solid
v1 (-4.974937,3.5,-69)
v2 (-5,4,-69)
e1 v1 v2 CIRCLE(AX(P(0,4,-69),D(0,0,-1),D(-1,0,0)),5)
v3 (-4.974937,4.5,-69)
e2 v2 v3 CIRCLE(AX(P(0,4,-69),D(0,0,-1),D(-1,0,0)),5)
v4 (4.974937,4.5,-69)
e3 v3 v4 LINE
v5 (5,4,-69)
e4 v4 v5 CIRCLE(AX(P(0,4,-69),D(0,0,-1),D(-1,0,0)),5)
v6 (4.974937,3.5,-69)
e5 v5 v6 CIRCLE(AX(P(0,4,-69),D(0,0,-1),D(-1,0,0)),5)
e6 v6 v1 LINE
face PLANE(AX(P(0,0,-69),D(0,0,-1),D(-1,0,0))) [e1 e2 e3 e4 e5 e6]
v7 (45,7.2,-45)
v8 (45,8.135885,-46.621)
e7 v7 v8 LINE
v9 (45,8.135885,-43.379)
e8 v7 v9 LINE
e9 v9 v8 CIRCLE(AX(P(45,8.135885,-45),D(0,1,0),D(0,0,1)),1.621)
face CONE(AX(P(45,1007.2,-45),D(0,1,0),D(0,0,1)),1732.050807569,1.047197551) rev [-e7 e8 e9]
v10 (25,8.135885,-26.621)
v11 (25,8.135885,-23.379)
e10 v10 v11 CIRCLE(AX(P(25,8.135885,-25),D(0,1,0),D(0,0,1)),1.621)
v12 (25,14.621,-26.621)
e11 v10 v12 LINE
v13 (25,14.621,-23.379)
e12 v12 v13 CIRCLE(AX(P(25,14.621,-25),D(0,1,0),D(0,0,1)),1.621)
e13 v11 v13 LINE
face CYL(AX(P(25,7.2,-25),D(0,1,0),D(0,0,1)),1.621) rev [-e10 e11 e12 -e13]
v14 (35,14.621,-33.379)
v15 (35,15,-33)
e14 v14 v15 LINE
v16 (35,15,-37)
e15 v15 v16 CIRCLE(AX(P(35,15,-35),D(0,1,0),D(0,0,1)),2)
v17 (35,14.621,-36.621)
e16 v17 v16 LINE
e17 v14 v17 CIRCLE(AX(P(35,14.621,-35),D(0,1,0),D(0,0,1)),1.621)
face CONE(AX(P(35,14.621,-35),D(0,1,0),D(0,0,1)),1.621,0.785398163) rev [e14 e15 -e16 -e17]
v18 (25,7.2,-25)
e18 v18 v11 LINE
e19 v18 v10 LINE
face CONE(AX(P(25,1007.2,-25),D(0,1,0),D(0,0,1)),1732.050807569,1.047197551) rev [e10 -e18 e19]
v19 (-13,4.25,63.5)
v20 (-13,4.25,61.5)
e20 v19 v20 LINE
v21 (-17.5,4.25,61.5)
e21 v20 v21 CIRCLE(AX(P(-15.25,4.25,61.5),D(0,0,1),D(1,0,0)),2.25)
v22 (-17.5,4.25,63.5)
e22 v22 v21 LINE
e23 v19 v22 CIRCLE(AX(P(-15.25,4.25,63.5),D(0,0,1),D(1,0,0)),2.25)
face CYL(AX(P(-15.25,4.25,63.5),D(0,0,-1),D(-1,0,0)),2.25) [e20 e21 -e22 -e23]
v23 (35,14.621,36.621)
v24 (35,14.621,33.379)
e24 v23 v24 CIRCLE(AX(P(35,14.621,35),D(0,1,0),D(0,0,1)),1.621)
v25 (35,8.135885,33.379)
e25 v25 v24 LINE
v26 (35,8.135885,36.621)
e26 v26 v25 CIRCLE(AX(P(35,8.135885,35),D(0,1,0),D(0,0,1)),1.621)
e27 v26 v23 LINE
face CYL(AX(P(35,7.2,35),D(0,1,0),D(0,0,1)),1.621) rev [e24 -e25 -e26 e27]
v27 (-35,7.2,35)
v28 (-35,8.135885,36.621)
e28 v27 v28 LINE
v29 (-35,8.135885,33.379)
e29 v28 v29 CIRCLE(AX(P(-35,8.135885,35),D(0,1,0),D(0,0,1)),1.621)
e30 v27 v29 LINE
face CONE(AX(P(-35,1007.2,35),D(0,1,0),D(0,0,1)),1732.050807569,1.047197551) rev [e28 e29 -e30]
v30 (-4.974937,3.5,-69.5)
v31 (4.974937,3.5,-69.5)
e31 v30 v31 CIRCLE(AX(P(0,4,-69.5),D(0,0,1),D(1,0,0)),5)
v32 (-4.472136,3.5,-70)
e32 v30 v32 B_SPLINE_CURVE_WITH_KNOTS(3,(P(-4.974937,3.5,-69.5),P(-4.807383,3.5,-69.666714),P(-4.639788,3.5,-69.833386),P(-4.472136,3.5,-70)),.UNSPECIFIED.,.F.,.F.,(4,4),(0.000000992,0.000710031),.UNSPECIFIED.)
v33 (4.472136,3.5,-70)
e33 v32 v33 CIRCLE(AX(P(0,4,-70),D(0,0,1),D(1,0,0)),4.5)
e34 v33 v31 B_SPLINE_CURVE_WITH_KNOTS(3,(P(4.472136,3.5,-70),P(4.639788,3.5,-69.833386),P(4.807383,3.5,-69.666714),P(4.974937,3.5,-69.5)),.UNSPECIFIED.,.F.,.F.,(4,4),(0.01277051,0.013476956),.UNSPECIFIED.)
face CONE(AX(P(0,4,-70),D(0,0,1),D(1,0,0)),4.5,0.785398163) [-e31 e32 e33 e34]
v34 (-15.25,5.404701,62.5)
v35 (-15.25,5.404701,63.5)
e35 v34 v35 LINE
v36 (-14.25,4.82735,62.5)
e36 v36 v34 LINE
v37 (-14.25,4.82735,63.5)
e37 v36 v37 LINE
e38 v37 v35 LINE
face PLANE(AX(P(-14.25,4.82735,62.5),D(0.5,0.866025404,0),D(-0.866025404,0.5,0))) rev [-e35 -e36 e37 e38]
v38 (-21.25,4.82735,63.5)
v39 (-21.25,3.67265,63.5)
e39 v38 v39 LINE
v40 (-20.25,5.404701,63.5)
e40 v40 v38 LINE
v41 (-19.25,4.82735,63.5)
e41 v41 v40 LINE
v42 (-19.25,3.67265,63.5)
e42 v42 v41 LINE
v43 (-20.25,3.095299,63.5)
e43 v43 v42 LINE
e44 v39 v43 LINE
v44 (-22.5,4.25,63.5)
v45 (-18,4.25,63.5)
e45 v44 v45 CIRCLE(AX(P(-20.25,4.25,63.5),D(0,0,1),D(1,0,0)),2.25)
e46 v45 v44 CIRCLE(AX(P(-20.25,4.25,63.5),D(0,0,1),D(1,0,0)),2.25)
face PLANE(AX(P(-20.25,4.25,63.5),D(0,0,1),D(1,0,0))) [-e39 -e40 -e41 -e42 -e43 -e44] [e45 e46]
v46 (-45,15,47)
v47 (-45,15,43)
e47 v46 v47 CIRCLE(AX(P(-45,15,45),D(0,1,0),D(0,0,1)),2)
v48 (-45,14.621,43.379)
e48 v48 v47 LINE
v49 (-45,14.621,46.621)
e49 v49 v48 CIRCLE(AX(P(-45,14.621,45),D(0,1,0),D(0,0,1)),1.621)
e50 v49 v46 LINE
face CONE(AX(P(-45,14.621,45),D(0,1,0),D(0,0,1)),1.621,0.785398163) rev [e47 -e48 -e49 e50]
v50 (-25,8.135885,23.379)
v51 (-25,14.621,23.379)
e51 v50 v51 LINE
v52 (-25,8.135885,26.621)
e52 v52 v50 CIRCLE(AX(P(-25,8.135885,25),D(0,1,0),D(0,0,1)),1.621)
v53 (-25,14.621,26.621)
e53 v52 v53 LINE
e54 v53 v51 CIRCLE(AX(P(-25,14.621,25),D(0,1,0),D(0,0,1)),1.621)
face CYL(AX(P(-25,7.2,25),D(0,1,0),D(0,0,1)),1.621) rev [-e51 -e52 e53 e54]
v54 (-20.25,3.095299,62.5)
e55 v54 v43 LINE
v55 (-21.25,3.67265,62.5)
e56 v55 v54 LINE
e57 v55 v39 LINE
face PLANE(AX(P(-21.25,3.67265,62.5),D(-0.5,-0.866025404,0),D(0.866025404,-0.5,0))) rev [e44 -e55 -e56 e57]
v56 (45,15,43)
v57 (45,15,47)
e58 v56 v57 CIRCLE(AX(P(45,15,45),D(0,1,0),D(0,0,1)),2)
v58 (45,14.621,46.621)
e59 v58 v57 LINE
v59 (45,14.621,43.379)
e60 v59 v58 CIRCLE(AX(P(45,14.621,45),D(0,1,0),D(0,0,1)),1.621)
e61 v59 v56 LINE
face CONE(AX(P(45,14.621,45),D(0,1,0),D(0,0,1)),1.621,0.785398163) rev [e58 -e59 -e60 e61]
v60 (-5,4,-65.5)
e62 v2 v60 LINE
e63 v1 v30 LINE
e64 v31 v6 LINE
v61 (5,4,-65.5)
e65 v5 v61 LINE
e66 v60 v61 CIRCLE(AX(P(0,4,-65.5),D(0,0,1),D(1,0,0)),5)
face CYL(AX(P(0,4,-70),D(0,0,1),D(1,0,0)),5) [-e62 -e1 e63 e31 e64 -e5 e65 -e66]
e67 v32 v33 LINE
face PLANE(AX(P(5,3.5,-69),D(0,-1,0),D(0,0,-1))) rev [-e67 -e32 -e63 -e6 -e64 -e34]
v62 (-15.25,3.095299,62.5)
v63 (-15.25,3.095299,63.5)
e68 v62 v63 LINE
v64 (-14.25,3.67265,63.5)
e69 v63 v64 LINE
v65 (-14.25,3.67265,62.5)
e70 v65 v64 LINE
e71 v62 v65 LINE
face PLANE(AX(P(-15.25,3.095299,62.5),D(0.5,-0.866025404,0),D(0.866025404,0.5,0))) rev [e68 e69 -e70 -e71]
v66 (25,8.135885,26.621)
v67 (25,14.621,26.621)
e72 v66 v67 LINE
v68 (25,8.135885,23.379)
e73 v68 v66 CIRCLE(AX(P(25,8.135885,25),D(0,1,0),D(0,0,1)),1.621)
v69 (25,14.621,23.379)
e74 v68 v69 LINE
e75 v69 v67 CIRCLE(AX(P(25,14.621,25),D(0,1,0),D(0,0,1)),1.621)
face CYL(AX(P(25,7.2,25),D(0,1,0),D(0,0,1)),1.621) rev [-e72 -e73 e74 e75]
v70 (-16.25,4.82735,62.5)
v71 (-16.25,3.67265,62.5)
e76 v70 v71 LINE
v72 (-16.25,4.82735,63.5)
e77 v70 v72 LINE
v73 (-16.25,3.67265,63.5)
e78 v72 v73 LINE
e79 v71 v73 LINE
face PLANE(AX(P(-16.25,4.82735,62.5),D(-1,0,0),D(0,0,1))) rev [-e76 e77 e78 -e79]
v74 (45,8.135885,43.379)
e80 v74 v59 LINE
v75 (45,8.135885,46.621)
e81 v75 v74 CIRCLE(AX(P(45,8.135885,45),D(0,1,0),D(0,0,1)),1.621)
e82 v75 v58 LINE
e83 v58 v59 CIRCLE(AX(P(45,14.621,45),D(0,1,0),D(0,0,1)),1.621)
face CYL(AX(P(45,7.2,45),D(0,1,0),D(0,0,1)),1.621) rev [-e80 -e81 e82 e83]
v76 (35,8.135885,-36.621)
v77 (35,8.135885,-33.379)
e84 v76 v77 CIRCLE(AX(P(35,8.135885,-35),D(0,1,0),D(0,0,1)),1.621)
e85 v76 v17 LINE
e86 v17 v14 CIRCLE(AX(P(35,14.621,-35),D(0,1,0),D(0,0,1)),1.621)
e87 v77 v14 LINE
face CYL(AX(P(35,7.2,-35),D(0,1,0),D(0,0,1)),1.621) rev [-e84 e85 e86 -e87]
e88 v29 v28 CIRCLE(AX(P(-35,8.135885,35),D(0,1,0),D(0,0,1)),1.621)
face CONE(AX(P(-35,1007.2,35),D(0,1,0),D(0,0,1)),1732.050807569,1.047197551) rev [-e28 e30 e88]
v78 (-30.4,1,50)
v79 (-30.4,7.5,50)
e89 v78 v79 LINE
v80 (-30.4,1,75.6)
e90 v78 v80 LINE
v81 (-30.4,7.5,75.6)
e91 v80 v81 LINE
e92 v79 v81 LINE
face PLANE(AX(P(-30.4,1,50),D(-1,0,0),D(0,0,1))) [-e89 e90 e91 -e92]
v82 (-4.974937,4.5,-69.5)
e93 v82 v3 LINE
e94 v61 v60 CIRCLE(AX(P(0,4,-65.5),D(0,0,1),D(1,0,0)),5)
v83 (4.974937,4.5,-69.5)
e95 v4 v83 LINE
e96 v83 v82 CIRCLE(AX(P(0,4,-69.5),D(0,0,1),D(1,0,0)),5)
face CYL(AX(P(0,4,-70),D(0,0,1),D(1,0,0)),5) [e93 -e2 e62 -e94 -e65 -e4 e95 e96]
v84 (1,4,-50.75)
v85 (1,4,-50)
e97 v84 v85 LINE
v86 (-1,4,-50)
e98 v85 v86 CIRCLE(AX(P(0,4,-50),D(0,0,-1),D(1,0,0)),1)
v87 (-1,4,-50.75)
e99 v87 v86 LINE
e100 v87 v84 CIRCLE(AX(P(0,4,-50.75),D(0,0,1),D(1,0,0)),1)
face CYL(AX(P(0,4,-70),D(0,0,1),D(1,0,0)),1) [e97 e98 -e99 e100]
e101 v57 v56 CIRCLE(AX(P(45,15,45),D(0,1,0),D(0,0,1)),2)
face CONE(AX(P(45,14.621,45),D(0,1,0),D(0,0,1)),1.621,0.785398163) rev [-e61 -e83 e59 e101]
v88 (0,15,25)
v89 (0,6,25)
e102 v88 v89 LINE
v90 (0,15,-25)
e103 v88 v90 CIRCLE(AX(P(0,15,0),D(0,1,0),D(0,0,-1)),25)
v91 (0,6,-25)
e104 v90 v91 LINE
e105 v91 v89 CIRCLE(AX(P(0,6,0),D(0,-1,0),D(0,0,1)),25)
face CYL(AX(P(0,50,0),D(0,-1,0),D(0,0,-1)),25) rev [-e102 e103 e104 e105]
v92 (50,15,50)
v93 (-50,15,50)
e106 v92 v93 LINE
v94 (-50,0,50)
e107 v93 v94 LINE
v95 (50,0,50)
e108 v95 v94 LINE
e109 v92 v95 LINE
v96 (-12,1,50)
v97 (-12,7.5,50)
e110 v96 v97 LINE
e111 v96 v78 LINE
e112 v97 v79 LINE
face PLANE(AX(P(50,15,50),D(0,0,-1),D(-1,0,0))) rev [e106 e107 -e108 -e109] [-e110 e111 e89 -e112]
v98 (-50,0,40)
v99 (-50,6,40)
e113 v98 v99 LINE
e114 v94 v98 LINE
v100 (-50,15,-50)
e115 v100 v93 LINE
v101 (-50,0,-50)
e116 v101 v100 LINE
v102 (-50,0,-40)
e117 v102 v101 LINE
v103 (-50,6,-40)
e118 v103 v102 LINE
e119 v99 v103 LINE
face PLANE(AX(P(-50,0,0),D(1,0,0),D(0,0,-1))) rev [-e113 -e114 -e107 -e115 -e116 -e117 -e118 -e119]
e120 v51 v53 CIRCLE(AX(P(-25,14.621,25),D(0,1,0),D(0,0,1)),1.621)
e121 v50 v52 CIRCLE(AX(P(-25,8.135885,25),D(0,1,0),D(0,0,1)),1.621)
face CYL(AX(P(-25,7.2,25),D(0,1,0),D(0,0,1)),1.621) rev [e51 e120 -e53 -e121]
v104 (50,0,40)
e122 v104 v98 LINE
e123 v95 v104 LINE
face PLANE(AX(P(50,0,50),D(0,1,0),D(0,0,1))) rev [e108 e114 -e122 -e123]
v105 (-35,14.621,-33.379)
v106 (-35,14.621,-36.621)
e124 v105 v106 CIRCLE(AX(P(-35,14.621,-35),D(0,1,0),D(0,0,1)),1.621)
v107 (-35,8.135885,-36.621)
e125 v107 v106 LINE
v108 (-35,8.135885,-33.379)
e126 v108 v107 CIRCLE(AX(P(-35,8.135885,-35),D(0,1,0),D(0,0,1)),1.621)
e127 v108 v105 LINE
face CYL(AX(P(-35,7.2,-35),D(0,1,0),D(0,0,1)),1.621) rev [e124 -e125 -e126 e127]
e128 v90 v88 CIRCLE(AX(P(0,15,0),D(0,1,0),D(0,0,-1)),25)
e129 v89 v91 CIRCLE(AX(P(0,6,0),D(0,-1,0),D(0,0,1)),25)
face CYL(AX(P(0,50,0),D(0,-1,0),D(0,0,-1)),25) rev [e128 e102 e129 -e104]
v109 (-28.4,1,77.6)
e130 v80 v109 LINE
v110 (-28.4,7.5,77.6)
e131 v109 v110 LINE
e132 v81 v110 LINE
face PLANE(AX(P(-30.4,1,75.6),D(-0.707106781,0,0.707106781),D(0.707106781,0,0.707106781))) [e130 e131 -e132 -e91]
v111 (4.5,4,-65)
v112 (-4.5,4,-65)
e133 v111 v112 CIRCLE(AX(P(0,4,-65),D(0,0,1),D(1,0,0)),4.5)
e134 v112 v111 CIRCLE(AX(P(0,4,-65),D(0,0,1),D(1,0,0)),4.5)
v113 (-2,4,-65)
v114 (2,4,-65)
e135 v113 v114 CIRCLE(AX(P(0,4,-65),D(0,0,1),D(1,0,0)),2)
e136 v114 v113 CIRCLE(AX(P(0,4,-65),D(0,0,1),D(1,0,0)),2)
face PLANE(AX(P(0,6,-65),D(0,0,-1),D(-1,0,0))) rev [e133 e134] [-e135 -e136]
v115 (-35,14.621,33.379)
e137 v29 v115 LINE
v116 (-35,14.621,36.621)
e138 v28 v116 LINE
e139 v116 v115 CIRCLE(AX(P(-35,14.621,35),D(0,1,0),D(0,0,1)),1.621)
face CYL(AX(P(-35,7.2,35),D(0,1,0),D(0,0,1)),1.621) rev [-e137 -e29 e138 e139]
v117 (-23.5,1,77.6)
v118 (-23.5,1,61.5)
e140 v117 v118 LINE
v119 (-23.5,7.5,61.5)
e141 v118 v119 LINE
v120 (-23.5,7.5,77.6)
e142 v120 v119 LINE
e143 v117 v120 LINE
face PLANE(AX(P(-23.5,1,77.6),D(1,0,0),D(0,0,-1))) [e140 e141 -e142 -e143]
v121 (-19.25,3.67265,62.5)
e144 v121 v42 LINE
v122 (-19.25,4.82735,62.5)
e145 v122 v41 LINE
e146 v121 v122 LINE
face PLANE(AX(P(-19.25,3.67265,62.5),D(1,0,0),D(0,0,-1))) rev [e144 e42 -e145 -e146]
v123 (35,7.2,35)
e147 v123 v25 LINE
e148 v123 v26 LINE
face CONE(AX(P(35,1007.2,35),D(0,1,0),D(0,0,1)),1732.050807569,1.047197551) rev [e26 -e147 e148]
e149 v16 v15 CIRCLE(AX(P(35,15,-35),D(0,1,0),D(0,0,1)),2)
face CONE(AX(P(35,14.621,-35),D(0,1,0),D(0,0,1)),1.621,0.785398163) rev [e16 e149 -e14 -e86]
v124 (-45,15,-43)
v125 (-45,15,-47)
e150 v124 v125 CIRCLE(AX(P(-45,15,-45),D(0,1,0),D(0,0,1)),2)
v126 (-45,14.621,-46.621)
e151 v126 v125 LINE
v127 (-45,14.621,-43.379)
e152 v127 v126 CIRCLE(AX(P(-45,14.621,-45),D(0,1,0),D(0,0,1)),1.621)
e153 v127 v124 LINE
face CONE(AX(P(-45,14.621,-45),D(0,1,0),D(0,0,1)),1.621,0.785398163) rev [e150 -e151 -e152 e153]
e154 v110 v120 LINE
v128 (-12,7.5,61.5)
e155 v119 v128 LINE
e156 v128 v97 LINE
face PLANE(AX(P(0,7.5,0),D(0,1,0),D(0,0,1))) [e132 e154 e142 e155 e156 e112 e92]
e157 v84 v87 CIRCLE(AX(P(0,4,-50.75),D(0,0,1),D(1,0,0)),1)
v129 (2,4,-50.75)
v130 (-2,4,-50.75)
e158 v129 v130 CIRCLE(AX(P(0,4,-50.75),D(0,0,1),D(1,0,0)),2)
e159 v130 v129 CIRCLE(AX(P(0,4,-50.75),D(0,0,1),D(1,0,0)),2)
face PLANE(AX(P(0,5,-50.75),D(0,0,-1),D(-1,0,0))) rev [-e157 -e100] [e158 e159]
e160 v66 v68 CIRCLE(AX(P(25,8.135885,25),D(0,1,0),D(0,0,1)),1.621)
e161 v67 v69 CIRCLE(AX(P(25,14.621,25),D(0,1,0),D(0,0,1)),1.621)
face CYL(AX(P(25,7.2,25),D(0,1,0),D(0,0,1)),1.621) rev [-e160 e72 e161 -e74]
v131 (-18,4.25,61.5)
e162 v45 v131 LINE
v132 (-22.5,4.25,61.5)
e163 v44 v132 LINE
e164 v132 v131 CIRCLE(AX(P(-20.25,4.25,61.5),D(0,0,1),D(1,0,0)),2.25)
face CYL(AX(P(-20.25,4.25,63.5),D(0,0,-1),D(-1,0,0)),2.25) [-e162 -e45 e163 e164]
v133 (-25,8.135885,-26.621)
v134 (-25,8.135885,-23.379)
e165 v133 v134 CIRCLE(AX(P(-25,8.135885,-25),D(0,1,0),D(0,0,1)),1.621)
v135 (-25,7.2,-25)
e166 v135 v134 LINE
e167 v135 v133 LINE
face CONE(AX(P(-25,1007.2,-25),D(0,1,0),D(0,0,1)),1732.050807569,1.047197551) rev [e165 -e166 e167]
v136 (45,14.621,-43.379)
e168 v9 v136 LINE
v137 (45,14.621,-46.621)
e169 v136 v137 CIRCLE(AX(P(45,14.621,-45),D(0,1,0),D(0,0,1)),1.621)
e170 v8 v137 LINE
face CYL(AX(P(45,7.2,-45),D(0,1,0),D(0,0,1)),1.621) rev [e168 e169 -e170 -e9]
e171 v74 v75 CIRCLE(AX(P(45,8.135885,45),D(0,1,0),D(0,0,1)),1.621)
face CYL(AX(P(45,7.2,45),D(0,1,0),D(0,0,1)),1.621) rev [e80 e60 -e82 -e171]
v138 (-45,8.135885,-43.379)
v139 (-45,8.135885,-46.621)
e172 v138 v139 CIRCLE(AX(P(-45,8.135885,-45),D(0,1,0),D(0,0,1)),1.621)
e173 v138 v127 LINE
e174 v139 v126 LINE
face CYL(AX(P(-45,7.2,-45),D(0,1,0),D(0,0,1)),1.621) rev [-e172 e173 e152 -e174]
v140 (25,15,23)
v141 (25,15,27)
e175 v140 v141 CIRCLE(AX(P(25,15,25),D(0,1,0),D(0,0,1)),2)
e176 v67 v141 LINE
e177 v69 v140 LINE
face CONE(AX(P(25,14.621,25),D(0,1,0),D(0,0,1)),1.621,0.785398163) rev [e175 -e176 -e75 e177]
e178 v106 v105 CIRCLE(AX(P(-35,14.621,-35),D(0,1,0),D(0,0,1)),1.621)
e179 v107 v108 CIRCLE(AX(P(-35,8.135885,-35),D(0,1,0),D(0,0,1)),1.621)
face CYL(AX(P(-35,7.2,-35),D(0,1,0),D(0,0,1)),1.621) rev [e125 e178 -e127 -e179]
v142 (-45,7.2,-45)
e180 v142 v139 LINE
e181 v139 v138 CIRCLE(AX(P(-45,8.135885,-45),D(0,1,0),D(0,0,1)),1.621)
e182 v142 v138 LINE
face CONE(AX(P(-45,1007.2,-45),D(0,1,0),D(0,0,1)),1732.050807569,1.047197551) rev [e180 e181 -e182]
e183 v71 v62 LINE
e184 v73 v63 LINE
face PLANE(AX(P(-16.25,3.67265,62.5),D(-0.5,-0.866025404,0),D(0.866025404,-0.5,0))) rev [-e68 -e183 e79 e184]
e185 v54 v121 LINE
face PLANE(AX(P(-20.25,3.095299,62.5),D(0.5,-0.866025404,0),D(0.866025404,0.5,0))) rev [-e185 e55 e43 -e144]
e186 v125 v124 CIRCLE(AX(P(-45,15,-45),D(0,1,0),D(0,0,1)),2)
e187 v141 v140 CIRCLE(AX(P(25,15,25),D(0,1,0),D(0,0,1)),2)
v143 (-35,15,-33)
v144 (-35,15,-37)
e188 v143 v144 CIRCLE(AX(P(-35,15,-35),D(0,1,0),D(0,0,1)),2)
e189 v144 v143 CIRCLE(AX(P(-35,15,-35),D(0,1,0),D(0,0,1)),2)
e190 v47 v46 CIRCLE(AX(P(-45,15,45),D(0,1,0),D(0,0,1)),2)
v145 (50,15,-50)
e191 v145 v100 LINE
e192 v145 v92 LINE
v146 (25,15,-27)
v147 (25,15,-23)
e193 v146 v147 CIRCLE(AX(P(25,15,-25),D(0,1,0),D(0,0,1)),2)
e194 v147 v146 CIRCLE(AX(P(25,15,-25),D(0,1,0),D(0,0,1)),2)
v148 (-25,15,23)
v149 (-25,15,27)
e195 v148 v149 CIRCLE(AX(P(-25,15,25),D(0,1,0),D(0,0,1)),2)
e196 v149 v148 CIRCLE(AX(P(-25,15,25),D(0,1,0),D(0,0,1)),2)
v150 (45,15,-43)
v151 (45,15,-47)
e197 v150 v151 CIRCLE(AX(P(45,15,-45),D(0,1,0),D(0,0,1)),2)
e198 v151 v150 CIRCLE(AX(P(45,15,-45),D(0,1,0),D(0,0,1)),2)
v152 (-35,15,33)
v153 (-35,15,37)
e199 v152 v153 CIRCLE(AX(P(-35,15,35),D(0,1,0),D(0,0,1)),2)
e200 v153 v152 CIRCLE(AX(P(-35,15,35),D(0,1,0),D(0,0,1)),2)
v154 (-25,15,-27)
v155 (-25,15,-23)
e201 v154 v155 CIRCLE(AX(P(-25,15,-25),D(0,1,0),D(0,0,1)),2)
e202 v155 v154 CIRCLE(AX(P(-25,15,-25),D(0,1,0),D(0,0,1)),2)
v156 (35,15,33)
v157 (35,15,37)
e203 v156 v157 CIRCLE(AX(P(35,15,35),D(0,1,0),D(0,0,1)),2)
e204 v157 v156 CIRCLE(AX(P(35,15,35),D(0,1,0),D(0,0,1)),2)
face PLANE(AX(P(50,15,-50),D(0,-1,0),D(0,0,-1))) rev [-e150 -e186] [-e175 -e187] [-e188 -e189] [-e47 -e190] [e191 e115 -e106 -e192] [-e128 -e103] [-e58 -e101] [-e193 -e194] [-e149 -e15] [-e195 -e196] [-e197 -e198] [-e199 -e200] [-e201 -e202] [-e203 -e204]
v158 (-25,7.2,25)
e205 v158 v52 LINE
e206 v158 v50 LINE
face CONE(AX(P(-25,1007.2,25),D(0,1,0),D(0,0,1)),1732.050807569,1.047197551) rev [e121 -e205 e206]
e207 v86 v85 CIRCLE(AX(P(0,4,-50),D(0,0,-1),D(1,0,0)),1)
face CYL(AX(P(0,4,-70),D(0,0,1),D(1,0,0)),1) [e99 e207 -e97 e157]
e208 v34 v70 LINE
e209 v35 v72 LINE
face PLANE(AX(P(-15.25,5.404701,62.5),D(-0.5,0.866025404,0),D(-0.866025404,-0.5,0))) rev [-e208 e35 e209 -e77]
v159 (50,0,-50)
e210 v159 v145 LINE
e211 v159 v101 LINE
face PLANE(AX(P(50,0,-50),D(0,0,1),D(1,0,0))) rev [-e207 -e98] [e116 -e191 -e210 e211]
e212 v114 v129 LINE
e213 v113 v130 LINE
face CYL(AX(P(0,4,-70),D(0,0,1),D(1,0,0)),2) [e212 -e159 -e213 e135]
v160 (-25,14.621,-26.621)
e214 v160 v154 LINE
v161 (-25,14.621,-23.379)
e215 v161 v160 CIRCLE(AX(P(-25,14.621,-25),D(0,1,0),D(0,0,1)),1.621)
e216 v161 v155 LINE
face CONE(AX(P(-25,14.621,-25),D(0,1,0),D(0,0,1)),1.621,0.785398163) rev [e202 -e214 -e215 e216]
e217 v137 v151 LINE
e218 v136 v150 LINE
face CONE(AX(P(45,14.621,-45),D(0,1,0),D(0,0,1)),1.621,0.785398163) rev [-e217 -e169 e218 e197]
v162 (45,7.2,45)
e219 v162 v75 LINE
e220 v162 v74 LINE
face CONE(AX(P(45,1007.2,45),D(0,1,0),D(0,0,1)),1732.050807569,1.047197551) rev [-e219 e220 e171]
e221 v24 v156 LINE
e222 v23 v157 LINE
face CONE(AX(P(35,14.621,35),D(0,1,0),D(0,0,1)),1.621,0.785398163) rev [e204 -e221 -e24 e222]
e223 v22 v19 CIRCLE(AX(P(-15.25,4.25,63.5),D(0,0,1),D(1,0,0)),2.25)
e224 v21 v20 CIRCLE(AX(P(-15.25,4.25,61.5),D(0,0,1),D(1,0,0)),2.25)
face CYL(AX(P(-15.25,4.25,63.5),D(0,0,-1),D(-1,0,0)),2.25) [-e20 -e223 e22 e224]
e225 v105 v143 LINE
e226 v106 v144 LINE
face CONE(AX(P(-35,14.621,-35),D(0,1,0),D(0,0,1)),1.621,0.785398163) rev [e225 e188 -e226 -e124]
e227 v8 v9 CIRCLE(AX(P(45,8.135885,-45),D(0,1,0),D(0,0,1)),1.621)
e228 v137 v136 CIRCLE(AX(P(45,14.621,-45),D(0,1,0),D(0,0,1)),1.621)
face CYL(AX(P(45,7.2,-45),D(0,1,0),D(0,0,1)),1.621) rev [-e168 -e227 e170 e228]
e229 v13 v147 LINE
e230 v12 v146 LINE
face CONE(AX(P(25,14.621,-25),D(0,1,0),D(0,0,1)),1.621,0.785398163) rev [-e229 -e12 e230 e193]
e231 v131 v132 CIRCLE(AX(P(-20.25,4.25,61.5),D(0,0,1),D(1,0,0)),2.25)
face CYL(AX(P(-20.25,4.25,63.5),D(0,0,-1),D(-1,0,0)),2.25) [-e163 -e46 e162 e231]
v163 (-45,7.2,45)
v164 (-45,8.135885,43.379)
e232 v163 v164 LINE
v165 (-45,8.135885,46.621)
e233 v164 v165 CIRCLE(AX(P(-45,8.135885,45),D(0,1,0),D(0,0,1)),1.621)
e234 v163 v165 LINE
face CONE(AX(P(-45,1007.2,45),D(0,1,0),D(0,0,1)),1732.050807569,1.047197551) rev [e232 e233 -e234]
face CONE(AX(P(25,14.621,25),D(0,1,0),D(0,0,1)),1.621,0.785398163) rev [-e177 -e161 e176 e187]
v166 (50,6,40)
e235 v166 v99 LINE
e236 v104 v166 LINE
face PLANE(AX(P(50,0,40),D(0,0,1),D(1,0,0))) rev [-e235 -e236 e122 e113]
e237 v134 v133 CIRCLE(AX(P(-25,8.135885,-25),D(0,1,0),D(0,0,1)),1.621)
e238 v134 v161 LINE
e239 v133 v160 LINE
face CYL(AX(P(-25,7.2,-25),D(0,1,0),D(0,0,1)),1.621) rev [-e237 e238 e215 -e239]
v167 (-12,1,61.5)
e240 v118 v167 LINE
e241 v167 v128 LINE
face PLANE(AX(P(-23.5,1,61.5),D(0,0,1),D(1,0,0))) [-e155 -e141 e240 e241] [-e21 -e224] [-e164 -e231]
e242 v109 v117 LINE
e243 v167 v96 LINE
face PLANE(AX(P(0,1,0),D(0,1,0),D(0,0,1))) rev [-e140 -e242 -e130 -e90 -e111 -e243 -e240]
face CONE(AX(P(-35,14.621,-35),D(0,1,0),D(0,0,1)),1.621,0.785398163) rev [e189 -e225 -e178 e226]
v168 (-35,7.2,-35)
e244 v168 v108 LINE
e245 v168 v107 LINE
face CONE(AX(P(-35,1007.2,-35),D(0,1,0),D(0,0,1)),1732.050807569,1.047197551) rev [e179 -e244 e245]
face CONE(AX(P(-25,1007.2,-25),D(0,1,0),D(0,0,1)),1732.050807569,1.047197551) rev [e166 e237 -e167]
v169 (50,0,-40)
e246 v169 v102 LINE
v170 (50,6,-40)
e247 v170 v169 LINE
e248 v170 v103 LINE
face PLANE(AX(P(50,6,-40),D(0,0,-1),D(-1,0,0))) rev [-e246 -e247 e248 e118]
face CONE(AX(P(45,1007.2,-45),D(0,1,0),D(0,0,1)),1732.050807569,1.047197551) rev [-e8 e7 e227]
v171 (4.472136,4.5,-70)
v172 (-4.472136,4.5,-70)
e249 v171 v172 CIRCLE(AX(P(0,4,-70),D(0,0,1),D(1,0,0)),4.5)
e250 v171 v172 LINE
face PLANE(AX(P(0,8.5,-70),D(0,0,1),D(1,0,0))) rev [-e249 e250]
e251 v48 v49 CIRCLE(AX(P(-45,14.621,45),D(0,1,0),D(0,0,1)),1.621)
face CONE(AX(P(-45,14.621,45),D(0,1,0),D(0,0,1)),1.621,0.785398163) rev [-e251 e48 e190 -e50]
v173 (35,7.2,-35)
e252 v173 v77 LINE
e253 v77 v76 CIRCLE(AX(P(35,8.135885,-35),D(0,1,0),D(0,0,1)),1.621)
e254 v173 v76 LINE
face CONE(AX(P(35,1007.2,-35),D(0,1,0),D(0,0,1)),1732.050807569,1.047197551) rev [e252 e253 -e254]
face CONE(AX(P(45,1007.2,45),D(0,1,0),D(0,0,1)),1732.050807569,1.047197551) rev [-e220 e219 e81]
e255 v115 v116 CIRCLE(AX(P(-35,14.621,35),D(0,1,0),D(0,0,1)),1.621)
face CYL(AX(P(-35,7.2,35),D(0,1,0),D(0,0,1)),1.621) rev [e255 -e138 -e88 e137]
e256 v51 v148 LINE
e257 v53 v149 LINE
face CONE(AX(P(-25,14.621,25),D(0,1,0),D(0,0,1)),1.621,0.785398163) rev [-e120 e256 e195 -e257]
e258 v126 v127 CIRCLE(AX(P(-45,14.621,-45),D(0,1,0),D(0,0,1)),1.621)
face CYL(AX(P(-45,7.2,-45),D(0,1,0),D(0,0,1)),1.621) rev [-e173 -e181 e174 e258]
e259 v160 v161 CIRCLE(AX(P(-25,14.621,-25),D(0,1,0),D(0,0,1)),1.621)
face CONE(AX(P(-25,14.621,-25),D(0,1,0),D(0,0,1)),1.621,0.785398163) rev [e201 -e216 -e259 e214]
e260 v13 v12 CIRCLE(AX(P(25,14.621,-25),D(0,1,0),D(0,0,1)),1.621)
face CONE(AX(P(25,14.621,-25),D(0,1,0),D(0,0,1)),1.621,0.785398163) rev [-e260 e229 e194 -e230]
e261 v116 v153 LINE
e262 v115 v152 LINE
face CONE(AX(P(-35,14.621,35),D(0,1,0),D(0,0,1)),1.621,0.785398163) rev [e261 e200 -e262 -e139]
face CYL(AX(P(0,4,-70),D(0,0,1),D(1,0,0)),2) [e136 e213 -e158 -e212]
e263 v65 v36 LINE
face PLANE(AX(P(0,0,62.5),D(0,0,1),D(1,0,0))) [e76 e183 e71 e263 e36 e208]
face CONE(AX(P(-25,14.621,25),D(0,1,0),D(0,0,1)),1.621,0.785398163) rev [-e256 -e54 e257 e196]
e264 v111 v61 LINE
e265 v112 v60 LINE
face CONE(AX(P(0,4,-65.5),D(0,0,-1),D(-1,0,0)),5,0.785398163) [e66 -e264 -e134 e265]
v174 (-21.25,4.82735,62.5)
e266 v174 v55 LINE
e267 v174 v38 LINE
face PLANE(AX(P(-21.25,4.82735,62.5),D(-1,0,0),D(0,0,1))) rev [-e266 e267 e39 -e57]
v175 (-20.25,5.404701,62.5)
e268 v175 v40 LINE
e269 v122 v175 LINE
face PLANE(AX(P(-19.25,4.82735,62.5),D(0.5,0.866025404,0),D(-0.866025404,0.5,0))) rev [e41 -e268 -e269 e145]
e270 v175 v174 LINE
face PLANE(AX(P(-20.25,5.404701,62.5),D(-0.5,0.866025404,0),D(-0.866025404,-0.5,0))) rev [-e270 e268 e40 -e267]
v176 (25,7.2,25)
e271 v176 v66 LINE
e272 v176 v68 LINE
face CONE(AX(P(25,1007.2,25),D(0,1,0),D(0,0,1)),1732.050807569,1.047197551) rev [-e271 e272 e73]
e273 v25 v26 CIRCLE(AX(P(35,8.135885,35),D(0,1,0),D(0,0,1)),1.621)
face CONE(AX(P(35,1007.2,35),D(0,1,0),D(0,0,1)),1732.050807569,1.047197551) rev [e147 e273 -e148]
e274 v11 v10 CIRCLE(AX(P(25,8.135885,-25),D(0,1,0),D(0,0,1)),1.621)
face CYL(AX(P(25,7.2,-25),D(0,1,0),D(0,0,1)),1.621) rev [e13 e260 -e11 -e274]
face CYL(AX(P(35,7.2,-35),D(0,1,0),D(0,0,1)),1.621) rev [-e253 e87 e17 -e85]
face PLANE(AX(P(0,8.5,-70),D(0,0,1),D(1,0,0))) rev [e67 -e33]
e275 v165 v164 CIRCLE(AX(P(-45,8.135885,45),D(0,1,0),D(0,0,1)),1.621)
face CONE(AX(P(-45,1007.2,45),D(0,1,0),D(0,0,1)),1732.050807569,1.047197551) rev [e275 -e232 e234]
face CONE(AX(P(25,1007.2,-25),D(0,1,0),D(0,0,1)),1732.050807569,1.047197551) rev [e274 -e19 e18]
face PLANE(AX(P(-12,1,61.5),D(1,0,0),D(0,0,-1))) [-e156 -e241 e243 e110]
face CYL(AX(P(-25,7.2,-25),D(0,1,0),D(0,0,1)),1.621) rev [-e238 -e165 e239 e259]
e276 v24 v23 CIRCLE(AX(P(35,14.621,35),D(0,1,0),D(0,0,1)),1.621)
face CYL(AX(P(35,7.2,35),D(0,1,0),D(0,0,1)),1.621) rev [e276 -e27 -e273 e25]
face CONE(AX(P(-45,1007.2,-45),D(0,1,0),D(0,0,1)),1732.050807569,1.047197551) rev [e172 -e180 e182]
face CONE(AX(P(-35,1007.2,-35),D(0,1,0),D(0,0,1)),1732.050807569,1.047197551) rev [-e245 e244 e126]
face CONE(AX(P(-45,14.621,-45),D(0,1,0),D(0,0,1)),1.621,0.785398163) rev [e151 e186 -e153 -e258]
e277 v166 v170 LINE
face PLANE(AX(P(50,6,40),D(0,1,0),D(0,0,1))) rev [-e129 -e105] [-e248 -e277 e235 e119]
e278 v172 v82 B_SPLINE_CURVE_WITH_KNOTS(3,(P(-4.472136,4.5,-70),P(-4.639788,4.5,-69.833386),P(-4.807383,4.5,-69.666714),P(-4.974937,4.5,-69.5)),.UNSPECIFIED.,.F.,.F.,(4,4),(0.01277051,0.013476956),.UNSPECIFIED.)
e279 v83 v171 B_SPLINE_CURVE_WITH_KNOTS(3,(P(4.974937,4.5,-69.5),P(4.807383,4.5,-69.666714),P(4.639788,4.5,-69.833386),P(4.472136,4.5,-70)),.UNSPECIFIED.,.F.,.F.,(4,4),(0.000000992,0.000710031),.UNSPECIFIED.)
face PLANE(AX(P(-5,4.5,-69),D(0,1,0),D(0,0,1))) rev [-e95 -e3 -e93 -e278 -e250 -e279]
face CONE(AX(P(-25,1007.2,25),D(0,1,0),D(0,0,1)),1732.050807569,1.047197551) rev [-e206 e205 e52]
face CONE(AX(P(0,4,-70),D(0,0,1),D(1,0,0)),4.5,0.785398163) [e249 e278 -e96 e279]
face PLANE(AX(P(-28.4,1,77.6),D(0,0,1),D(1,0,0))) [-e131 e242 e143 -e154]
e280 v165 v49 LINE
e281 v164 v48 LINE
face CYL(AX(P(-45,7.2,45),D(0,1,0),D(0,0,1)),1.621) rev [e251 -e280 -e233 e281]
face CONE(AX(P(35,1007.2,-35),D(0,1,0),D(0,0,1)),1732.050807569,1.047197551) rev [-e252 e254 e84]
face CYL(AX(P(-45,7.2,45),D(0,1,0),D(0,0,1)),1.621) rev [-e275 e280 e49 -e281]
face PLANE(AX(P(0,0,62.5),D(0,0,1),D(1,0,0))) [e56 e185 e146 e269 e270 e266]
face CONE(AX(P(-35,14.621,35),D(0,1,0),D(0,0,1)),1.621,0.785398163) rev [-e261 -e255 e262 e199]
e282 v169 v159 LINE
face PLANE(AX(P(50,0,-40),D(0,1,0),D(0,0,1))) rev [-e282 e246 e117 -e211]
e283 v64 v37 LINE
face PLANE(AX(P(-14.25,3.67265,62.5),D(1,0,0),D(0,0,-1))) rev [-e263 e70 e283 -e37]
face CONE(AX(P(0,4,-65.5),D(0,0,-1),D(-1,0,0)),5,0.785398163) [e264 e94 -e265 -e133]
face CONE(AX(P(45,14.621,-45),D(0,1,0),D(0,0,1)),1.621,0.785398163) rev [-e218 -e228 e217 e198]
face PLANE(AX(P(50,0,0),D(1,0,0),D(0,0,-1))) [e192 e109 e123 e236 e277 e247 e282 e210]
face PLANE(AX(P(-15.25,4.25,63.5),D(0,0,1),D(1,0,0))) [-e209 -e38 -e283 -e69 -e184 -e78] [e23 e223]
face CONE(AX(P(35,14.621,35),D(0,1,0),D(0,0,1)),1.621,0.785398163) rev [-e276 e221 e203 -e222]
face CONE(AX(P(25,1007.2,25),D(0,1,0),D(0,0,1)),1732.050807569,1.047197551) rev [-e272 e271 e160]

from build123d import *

# Parameters (mm, degrees)
EXTRUDE_1_DEPTH      = 50
EXTRUDE_1_DEPTH_BACK = 50
EXTRUDE_2_DEPTH      = 6.5
SKETCH_16_R          = 25
CUT_EXTRUDE_1_DEPTH  = 50
SKETCH_17_W          = 10
SKETCH_17_H          = 1
CUT_EXTRUDE_2_DEPTH  = 1
SKETCH_18_R          = 2.25
EXTRUDE_3_DEPTH      = 2
SKETCH_19_R          = 2.25
EXTRUDE_4_DEPTH      = 2
CUT_EXTRUDE_3_DEPTH  = 1
CUT_EXTRUDE_4_DEPTH  = 1


with BuildPart() as part:
    # 草图1 → 凸台-拉伸1 (new, two sides: drawn at the far end of the back side and taken through both)
    with BuildSketch(Plane(origin=(0, 0, 0), x_dir=(0, 0, -1), z_dir=(1, 0, 0)).offset(-EXTRUDE_1_DEPTH_BACK)):
        Polygon((-50, 15), (-50, 0), (-40, 0), (-40, 6), (40, 6), (40, 0), (50, 0), (50, 15), align=None)
    extrude(amount=EXTRUDE_1_DEPTH + EXTRUDE_1_DEPTH_BACK)

    # 草图2 → 旋转1 (revolve)
    with BuildSketch(Plane(origin=(0, 0, 0), x_dir=(0, 0, -1), z_dir=(1, 0, 0)), mode=Mode.PRIVATE) as revolve_1_sk:
        Polygon((50, 4), (50, 5), (50.75, 5), (50.75, 6), (65, 6), (65, 8.5), (65.5, 9), (69.5, 9), (70, 8.5), (70, 4), align=None)
    revolve(revolve_1_sk.sketch.rotate(Axis((0, 4, -70), (0, 0, 1)), 270), axis=Axis((0, 4, -70), (0, 0, 1)))

    # 草图3 → 凸台-拉伸2 (add)
    with BuildSketch(Plane(origin=(0, 7.5, 0), x_dir=(-1, 0, 0), z_dir=(0, 1, 0))):
        Polygon((30.4, 50), (30.4, 75.6), (28.4, 77.6), (23.5, 77.6), (23.5, 61.5), (12, 61.5), (12, 50), align=None)
    extrude(amount=-EXTRUDE_2_DEPTH)

    # 草图4 → 切除-旋转1 (revolve, cut)
    with BuildSketch(Plane.XY.offset(45), mode=Mode.PRIVATE) as cut_revolve_1_sk:
        Polygon((-45, 15), (-43, 15), (-43.379, 14.621), (-43.379, 8.135884786), (-45, 7.2), align=None)
    revolve(cut_revolve_1_sk.sketch.rotate(Axis((-45, 7.2, 45), (0, 1, 0)), 270), axis=Axis((-45, 7.2, 45), (0, 1, 0)), mode=Mode.SUBTRACT)

    # 草图5 → 切除-旋转2 (revolve, cut)
    with BuildSketch(Plane.XY.offset(45), mode=Mode.PRIVATE) as cut_revolve_2_sk:
        Polygon((45, 15), (47, 15), (46.621, 14.621), (46.621, 8.135884786), (45, 7.2), align=None)
    revolve(cut_revolve_2_sk.sketch.rotate(Axis((45, 7.2, 45), (0, 1, 0)), 270), axis=Axis((45, 7.2, 45), (0, 1, 0)), mode=Mode.SUBTRACT)

    # 草图6 → 切除-旋转3 (revolve, cut)
    with BuildSketch(Plane.XY.offset(-45), mode=Mode.PRIVATE) as cut_revolve_3_sk:
        Polygon((-45, 15), (-43, 15), (-43.379, 14.621), (-43.379, 8.135884786), (-45, 7.2), align=None)
    revolve(cut_revolve_3_sk.sketch.rotate(Axis((-45, 7.2, -45), (0, 1, 0)), 270), axis=Axis((-45, 7.2, -45), (0, 1, 0)), mode=Mode.SUBTRACT)

    # 草图7 → 切除-旋转4 (revolve, cut)
    with BuildSketch(Plane.XY.offset(-45), mode=Mode.PRIVATE) as cut_revolve_4_sk:
        Polygon((45, 15), (47, 15), (46.621, 14.621), (46.621, 8.135884786), (45, 7.2), align=None)
    revolve(cut_revolve_4_sk.sketch.rotate(Axis((45, 7.2, -45), (0, 1, 0)), 270), axis=Axis((45, 7.2, -45), (0, 1, 0)), mode=Mode.SUBTRACT)

    # 草图8 → 切除-旋转5 (revolve, cut)
    with BuildSketch(Plane.XY.offset(-35), mode=Mode.PRIVATE) as cut_revolve_5_sk:
        Polygon((35, 15), (37, 15), (36.621, 14.621), (36.621, 8.135884786), (35, 7.2), align=None)
    revolve(cut_revolve_5_sk.sketch.rotate(Axis((35, 7.2, -35), (0, 1, 0)), 270), axis=Axis((35, 7.2, -35), (0, 1, 0)), mode=Mode.SUBTRACT)

    # 草图9 → 切除-旋转6 (revolve, cut)
    with BuildSketch(Plane.XY.offset(-35), mode=Mode.PRIVATE) as cut_revolve_6_sk:
        Polygon((-35, 15), (-33, 15), (-33.379, 14.621), (-33.379, 8.135884786), (-35, 7.2), align=None)
    revolve(cut_revolve_6_sk.sketch.rotate(Axis((-35, 7.2, -35), (0, 1, 0)), 270), axis=Axis((-35, 7.2, -35), (0, 1, 0)), mode=Mode.SUBTRACT)

    # 草图10 → 切除-旋转7 (revolve, cut)
    with BuildSketch(Plane.XY.offset(35), mode=Mode.PRIVATE) as cut_revolve_7_sk:
        Polygon((-35, 15), (-33, 15), (-33.379, 14.621), (-33.379, 8.135884786), (-35, 7.2), align=None)
    revolve(cut_revolve_7_sk.sketch.rotate(Axis((-35, 7.2, 35), (0, 1, 0)), 270), axis=Axis((-35, 7.2, 35), (0, 1, 0)), mode=Mode.SUBTRACT)

    # 草图11 → 切除-旋转8 (revolve, cut)
    with BuildSketch(Plane.XY.offset(35), mode=Mode.PRIVATE) as cut_revolve_8_sk:
        Polygon((35, 15), (37, 15), (36.621, 14.621), (36.621, 8.135884786), (35, 7.2), align=None)
    revolve(cut_revolve_8_sk.sketch.rotate(Axis((35, 7.2, 35), (0, 1, 0)), 270), axis=Axis((35, 7.2, 35), (0, 1, 0)), mode=Mode.SUBTRACT)

    # 草图12 → 切除-旋转9 (revolve, cut)
    with BuildSketch(Plane.XY.offset(-25), mode=Mode.PRIVATE) as cut_revolve_9_sk:
        Polygon((25, 15), (27, 15), (26.621, 14.621), (26.621, 8.135884786), (25, 7.2), align=None)
    revolve(cut_revolve_9_sk.sketch.rotate(Axis((25, 7.2, -25), (0, 1, 0)), 270), axis=Axis((25, 7.2, -25), (0, 1, 0)), mode=Mode.SUBTRACT)

    # 草图13 → 切除-旋转10 (revolve, cut)
    with BuildSketch(Plane.XY.offset(-25), mode=Mode.PRIVATE) as cut_revolve_10_sk:
        Polygon((-25, 15), (-23, 15), (-23.379, 14.621), (-23.379, 8.135884786), (-25, 7.2), align=None)
    revolve(cut_revolve_10_sk.sketch.rotate(Axis((-25, 7.2, -25), (0, 1, 0)), 270), axis=Axis((-25, 7.2, -25), (0, 1, 0)), mode=Mode.SUBTRACT)

    # 草图14 → 切除-旋转11 (revolve, cut)
    with BuildSketch(Plane.XY.offset(25), mode=Mode.PRIVATE) as cut_revolve_11_sk:
        Polygon((-25, 15), (-23, 15), (-23.379, 14.621), (-23.379, 8.135884786), (-25, 7.2), align=None)
    revolve(cut_revolve_11_sk.sketch.rotate(Axis((-25, 7.2, 25), (0, 1, 0)), 270), axis=Axis((-25, 7.2, 25), (0, 1, 0)), mode=Mode.SUBTRACT)

    # 草图15 → 切除-旋转12 (revolve, cut)
    with BuildSketch(Plane.XY.offset(25), mode=Mode.PRIVATE) as cut_revolve_12_sk:
        Polygon((25, 15), (27, 15), (26.621, 14.621), (26.621, 8.135884786), (25, 7.2), align=None)
    revolve(cut_revolve_12_sk.sketch.rotate(Axis((25, 7.2, 25), (0, 1, 0)), 270), axis=Axis((25, 7.2, 25), (0, 1, 0)), mode=Mode.SUBTRACT)

    # 草图16 → 切除-拉伸1 (cut)
    with BuildSketch(Plane(origin=(0, 0, 0), x_dir=(-1, 0, 0), z_dir=(0, 1, 0))):
        with Locations(Location((0, 0, 0), (0, 0, 270))):
            Circle(SKETCH_16_R)
    extrude(amount=CUT_EXTRUDE_1_DEPTH, mode=Mode.SUBTRACT)

    # 草图17 → 切除-拉伸2 (cut)
    with BuildSketch(Plane(origin=(0, 0, -70), x_dir=(-1, 0, 0), z_dir=(0, 0, -1))):
        with Locations((0, 4)):
            Rectangle(SKETCH_17_W, SKETCH_17_H)
    extrude(amount=-CUT_EXTRUDE_2_DEPTH, mode=Mode.SUBTRACT)

    # 草图18 → 凸台-拉伸3 (add)
    with BuildSketch(Plane.XY.offset(61.5)):
        with Locations((-20.25, 4.25)):
            Circle(SKETCH_18_R)
    extrude(amount=EXTRUDE_3_DEPTH)

    # 草图19 → 凸台-拉伸4 (add)
    with BuildSketch(Plane.XY.offset(61.5)):
        with Locations((-15.25, 4.25)):
            Circle(SKETCH_19_R)
    extrude(amount=EXTRUDE_4_DEPTH)

    # 草图20 → 切除-拉伸3 (cut)
    with BuildSketch(Plane.XY.offset(63.5)):
        Polygon((-16.25, 3.672649731), (-15.25, 3.095299462), (-14.25, 3.672649731), (-14.25, 4.827350269), (-15.25, 5.404700538), (-16.25, 4.827350269), align=None)
    extrude(amount=-CUT_EXTRUDE_3_DEPTH, mode=Mode.SUBTRACT)

    # 草图21 → 切除-拉伸4 (cut)
    with BuildSketch(Plane.XY.offset(63.5)):
        Polygon((-21.25, 3.672649731), (-20.25, 3.095299462), (-19.25, 3.672649731), (-19.25, 4.827350269), (-20.25, 5.404700538), (-21.25, 4.827350269), align=None)
    extrude(amount=-CUT_EXTRUDE_4_DEPTH, mode=Mode.SUBTRACT)


solid = part.part
